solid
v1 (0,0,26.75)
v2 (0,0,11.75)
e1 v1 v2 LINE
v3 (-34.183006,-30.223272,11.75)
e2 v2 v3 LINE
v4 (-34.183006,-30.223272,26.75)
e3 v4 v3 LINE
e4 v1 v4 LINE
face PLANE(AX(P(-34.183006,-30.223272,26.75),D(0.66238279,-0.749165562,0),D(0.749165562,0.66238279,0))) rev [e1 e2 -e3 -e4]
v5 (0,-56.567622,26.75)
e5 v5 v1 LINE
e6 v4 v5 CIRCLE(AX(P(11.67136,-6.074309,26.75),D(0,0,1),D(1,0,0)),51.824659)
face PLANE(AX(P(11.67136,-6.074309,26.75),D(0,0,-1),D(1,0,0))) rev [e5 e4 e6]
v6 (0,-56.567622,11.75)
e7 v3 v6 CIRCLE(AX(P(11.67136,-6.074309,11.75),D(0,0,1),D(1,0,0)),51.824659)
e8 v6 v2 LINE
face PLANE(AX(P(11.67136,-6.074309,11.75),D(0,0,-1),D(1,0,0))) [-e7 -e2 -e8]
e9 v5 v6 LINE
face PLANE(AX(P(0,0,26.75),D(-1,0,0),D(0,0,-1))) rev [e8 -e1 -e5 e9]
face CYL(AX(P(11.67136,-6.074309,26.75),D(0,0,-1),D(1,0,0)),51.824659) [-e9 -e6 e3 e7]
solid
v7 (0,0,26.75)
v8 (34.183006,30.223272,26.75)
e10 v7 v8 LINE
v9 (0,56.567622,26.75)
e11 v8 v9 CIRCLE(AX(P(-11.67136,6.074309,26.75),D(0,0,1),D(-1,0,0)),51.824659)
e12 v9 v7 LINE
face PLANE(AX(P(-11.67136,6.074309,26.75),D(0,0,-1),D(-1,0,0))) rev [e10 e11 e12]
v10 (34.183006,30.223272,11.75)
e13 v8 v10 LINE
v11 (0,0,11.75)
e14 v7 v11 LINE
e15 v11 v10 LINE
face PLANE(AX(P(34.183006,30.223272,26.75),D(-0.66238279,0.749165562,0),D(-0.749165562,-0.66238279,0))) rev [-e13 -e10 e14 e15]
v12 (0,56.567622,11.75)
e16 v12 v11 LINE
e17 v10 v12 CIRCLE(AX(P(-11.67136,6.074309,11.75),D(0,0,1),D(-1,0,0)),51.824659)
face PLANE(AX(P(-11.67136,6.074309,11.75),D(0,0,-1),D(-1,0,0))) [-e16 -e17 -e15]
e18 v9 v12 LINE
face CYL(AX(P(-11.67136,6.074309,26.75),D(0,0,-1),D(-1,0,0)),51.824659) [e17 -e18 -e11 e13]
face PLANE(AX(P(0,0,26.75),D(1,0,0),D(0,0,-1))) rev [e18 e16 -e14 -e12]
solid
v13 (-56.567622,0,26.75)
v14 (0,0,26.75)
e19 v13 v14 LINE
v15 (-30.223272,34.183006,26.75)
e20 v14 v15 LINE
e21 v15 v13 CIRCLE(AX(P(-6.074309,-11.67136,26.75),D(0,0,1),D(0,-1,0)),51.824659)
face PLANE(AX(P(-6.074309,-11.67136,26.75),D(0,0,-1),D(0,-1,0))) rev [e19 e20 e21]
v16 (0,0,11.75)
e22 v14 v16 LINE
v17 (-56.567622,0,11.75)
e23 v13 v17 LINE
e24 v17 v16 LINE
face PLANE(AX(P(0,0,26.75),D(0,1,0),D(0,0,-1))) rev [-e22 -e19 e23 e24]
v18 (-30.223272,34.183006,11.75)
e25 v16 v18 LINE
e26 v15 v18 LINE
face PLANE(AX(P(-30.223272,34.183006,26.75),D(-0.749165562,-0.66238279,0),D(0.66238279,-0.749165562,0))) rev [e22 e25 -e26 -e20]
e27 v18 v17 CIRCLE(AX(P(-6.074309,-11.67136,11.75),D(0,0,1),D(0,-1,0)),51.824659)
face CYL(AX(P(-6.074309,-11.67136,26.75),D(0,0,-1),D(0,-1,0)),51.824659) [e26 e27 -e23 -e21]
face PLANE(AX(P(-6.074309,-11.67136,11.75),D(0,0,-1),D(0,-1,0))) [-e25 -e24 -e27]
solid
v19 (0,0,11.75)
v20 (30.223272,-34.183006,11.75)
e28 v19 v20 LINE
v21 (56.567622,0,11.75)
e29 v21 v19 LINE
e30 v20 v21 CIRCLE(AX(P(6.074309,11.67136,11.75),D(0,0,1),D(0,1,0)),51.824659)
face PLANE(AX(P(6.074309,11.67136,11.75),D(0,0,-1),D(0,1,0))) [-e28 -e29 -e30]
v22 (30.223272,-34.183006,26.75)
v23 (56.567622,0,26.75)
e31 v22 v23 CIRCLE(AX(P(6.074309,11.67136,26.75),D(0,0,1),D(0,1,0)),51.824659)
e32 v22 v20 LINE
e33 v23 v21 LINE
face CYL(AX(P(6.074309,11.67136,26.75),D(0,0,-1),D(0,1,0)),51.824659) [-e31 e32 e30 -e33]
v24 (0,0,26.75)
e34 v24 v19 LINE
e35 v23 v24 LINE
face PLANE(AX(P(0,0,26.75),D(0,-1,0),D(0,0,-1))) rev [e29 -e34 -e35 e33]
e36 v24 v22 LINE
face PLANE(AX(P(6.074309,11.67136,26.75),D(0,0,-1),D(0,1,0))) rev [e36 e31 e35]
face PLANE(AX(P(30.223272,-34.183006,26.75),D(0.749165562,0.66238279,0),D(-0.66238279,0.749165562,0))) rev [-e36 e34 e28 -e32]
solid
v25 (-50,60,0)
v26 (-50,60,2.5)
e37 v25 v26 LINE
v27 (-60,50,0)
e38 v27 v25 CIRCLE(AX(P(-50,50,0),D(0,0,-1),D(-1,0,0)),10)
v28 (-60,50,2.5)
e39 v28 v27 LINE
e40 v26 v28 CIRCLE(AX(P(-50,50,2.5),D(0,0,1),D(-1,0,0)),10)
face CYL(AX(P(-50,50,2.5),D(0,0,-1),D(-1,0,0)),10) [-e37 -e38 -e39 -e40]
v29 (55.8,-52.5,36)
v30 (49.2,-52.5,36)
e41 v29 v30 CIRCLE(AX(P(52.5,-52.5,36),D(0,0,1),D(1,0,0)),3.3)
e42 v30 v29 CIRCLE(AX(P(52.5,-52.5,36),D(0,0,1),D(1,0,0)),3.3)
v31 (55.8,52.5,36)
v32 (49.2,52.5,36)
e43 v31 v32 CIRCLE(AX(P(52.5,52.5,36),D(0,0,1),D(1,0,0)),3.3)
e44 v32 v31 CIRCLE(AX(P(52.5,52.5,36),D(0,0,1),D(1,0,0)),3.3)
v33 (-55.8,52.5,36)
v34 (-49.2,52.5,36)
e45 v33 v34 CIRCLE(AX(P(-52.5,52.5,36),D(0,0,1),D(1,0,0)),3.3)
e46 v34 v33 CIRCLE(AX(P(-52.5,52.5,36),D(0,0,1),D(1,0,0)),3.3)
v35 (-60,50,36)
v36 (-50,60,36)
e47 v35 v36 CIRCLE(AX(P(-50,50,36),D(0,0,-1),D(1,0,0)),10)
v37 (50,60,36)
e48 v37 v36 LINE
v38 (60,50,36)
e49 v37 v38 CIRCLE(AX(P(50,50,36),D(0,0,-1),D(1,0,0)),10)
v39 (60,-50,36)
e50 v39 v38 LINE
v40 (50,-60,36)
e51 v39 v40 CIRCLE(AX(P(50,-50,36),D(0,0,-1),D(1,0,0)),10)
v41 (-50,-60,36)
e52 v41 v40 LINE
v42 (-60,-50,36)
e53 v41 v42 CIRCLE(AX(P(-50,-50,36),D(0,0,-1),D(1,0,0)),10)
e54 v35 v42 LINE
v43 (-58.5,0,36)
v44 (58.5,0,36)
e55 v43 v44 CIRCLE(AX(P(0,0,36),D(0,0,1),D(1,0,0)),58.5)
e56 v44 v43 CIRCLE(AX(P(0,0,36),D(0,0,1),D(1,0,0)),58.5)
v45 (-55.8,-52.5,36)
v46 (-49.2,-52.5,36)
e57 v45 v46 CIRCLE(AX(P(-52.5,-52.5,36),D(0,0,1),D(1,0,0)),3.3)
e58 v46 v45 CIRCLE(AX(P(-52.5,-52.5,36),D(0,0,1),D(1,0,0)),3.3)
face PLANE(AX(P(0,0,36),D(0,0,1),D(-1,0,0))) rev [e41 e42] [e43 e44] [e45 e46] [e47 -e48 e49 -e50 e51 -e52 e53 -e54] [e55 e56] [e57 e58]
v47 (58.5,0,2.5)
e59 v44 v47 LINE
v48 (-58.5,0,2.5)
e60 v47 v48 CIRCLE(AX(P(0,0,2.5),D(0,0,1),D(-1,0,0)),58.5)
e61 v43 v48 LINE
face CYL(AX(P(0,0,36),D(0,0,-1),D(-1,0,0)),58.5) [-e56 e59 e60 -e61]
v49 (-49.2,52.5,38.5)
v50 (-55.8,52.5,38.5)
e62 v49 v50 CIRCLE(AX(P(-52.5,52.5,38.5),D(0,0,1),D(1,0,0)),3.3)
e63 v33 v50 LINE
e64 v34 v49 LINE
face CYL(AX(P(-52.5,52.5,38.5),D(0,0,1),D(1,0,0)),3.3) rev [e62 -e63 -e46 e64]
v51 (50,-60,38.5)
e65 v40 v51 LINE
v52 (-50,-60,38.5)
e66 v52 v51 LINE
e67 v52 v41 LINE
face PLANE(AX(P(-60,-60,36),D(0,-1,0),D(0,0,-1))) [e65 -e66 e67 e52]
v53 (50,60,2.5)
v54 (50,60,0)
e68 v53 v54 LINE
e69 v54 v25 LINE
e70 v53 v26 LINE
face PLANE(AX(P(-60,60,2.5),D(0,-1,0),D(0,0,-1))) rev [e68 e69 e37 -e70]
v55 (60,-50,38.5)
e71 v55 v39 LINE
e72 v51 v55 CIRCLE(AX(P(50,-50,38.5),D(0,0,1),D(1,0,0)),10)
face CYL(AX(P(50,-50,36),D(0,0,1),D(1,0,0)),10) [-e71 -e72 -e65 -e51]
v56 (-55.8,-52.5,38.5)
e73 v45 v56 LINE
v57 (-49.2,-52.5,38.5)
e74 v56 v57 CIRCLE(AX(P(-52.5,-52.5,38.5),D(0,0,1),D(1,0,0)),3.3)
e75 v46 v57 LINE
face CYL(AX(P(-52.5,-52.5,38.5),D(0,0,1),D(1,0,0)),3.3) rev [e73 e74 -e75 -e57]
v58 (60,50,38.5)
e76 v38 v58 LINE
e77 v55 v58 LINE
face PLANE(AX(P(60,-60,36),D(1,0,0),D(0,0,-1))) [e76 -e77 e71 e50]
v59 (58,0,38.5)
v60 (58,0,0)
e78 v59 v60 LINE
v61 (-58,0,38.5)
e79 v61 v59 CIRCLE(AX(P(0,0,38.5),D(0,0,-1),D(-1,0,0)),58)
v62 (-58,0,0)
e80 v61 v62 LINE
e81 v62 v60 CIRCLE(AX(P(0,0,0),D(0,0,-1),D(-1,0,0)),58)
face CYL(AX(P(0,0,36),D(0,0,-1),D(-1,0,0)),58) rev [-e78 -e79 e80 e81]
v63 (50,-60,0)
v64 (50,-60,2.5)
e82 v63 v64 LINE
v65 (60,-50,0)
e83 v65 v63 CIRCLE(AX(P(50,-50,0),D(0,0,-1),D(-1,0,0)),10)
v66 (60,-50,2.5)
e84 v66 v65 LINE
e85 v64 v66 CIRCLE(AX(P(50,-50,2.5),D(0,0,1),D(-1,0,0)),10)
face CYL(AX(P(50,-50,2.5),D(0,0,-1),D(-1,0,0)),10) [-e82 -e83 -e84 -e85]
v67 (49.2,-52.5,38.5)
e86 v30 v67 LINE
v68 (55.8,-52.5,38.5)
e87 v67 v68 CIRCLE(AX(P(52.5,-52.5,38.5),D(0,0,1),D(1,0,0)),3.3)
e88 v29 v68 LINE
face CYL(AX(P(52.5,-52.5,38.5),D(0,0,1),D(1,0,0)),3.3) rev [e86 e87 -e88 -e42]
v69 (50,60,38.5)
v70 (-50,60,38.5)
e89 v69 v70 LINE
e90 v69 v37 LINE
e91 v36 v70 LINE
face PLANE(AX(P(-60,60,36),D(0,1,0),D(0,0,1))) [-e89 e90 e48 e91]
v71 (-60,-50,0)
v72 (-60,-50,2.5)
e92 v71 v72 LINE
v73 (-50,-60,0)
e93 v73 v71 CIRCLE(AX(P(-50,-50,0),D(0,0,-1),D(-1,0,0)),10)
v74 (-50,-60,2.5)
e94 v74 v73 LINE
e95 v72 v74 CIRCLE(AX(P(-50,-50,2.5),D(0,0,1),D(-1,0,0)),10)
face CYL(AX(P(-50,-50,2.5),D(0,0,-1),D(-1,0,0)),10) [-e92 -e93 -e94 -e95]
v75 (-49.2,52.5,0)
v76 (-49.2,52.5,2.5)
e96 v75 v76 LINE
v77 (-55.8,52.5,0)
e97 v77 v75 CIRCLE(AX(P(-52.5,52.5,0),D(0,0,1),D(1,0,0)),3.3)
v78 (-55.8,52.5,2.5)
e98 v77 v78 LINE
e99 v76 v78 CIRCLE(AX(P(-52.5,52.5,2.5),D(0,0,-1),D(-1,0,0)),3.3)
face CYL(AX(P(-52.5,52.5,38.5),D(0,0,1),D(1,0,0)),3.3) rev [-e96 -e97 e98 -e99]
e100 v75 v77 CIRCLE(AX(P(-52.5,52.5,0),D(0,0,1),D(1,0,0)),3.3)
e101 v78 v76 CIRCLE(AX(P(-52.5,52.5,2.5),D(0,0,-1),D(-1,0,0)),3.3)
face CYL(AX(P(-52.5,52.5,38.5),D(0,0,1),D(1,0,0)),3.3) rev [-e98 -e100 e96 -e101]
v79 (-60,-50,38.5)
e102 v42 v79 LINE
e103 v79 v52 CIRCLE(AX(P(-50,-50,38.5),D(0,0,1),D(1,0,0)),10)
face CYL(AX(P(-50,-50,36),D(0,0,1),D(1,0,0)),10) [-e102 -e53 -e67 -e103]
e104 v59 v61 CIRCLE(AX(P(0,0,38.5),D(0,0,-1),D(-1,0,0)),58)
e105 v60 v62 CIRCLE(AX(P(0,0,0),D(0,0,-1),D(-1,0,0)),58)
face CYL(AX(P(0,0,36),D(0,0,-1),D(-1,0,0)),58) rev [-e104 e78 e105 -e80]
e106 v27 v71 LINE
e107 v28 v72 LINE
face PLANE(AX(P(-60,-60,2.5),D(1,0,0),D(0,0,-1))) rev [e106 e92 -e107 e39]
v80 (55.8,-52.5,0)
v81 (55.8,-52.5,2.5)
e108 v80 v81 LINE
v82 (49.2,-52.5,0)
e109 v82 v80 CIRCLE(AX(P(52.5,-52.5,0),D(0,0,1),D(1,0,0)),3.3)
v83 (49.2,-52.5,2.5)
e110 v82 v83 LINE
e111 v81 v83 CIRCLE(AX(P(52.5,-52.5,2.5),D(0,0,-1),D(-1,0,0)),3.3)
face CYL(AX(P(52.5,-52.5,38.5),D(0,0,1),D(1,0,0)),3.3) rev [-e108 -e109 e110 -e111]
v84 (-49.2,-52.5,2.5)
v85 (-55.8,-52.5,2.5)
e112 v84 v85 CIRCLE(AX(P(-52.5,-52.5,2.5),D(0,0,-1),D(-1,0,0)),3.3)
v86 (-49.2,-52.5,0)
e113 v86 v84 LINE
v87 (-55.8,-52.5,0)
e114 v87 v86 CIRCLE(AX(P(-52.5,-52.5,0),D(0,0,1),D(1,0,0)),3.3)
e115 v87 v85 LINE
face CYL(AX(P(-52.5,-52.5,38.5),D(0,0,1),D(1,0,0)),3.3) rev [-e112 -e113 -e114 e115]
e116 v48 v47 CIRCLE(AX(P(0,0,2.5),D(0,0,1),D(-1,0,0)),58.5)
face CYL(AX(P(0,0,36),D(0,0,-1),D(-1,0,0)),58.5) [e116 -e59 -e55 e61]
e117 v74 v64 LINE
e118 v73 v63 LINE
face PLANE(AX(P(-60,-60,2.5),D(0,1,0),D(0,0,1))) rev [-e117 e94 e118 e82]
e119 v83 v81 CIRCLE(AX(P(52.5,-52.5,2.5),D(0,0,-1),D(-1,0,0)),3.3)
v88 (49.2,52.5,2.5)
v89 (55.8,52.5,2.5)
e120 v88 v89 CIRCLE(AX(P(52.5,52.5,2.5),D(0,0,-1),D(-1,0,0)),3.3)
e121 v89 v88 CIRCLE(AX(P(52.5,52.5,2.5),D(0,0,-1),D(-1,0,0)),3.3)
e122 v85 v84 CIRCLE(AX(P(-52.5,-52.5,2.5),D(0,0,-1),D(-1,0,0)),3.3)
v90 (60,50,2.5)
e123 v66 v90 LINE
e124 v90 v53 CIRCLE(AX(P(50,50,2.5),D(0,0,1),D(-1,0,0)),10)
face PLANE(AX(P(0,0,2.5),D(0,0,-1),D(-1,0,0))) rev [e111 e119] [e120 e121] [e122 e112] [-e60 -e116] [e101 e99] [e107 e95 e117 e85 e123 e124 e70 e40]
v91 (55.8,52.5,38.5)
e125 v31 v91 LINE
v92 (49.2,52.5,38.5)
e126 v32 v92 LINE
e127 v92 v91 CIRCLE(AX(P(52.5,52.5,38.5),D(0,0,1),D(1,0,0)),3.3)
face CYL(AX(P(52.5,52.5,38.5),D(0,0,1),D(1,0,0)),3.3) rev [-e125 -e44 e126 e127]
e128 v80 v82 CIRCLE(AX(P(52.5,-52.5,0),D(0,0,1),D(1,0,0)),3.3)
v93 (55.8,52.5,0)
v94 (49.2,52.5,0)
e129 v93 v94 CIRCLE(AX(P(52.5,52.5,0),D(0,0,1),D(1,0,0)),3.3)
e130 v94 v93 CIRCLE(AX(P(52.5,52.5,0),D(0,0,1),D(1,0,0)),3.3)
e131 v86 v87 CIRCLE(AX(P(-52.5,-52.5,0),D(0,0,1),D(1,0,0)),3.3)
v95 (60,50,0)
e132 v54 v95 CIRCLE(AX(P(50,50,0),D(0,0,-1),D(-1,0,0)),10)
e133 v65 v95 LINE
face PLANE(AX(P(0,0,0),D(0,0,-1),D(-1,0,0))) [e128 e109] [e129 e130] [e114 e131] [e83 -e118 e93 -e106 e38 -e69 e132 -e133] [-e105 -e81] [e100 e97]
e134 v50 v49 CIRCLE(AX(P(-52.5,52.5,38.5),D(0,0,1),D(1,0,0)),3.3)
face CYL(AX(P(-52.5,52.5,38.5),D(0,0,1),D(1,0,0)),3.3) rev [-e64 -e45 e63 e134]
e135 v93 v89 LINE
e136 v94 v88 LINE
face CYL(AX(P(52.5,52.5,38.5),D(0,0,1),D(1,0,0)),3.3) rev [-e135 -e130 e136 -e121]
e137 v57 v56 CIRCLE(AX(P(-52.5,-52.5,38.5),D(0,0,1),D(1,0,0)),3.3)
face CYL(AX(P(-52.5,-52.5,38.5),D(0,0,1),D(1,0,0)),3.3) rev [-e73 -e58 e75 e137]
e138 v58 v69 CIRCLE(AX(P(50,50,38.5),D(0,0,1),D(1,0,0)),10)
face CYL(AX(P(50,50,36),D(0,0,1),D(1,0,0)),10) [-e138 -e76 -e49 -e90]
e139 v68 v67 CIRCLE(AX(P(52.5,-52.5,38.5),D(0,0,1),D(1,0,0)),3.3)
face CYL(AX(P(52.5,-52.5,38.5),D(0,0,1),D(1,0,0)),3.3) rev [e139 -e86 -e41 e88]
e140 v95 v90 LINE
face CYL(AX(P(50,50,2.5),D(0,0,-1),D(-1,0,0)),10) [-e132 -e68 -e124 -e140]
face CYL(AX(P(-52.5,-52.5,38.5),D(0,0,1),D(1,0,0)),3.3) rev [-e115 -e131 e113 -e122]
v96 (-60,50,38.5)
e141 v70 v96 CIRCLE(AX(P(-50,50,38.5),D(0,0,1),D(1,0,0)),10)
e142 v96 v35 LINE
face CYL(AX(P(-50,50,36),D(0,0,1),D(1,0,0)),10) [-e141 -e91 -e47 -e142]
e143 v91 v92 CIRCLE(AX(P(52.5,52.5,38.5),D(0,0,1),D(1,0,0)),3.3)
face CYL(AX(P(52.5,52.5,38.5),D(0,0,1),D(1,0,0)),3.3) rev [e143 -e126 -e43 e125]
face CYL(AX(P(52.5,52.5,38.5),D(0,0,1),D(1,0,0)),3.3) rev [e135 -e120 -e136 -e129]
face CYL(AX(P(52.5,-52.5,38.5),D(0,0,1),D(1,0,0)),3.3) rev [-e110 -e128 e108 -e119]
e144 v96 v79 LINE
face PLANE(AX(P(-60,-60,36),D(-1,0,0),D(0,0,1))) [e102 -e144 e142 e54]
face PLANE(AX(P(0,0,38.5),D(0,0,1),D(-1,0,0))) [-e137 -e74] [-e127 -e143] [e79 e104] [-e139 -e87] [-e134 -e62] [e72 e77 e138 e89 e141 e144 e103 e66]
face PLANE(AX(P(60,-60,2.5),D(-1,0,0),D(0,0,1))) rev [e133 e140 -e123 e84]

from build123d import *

# Parameters (mm, degrees)
SKETCH_1_W                  = 120
SKETCH_1_H                  = 120
EXTRUDE_1_DEPTH             = 2.5
SKETCH_2_R                  = 58.5
SKETCH_2_R_2                = 56.5
EXTRUDE_2_DEPTH             = 33.5
SKETCH_4_R                  = 58
CUT_EXTRUDE_1_DEPTH         = 93.173748974
FILLET_1_R                  = 10
FILLET_1_OF_MIRROR_1_R      = 10
EXTRUDE_3_DEPTH             = 7.5
PATTERN_CIRCULAR_2_COUNT    = 4
SKETCH_9_W                  = 3.3
SKETCH_9_H                  = 38.5
HOLE_WIZARD_M6_1_AT_2_COUNT = 2
HOLE_WIZARD_M6_1_AT_2_PITCH = 105
HOLE_WIZARD_M6_1_AT_3_COUNT = 2
HOLE_WIZARD_M6_1_AT_3_PITCH = 148.492424049
HOLE_WIZARD_M6_1_AT_4_COUNT = 2
HOLE_WIZARD_M6_1_AT_4_PITCH = 105


with BuildPart() as part:
    # 草图1 → 凸台-拉伸1 (new body)
    with BuildSketch(Plane.XY):
        Rectangle(SKETCH_1_W, SKETCH_1_H)
    extrude_1 = extrude(amount=EXTRUDE_1_DEPTH)

    # 草图2 → 凸台-拉伸2 (add)
    with BuildSketch(Plane.XY.offset(2.5)):
        with Locations(Location((0, 0, 0), (0, 0, 180))):
            Circle(SKETCH_2_R)
        Circle(SKETCH_2_R_2, mode=Mode.SUBTRACT)
    extrude(amount=EXTRUDE_2_DEPTH)

    # 草图4 → 切除-拉伸1 (cut, through all)
    with BuildSketch(Plane(origin=(0, 0, 0), x_dir=(-1, 0, 0), z_dir=(0, 0, -1))):
        Circle(SKETCH_4_R)
    cut_extrude_1 = extrude(amount=-CUT_EXTRUDE_1_DEPTH, mode=Mode.SUBTRACT)

    # 圆角1
    fillet_1_edges = [part.edges().sort_by_distance(p)[0] for p in [
        (60, -60, 1.25),
        (-60, -60, 1.25),
        (-60, 60, 1.25),
        (60, 60, 1.25),
    ]]
    fillet(fillet_1_edges, radius=FILLET_1_R)

    # 镜向1: 凸台-拉伸1, 切除-拉伸1 across plane
    add(extrude_1.mirror(Plane.XY.offset(19.25)))
    add(cut_extrude_1.mirror(Plane.XY.offset(19.25)), mode=Mode.SUBTRACT)

    # 圆角1 of 镜向1
    fillet_1_of_mirror_1_edges = [part.edges().sort_by_distance(p)[0] for p in [
        (60, -60, 37.25),
        (-60, -60, 37.25),
        (-60, 60, 37.25),
        (60, 60, 37.25),
    ]]
    fillet(fillet_1_of_mirror_1_edges, radius=FILLET_1_OF_MIRROR_1_R)

    # 草图9 → M6 间隙孔1 (revolve, cut)
    with BuildSketch(Plane(origin=(-52.5, 52.5, 38.5), x_dir=(0, -1, 0), z_dir=(1, 0, 0))):
        with Locations((1.65, 19.25)):
            Rectangle(SKETCH_9_W, SKETCH_9_H)
    hole_wizard_m6_1 = revolve(axis=Axis((-52.5, 52.5, 44.85), (0, 0, -1)), mode=Mode.SUBTRACT)

    # M6 间隙孔1 at 2: M6 间隙孔1 ×2
    with Locations(*[(i * HOLE_WIZARD_M6_1_AT_2_PITCH, 0, 0) for i in range(1, HOLE_WIZARD_M6_1_AT_2_COUNT)]):
        add(hole_wizard_m6_1, mode=Mode.SUBTRACT)

    # M6 间隙孔1 at 3: M6 间隙孔1 ×2
    with Locations(*[Vector(0.7071067811865476, -0.7071067811865476, 0) * (i * HOLE_WIZARD_M6_1_AT_3_PITCH) for i in range(1, HOLE_WIZARD_M6_1_AT_3_COUNT)]):
        add(hole_wizard_m6_1, mode=Mode.SUBTRACT)

    # M6 间隙孔1 at 4: M6 间隙孔1 ×2
    with Locations(*[(0, -i * HOLE_WIZARD_M6_1_AT_4_PITCH, 0) for i in range(1, HOLE_WIZARD_M6_1_AT_4_COUNT)]):
        add(hole_wizard_m6_1, mode=Mode.SUBTRACT)


with BuildPart() as body_2:
    # 草图6 → 凸台-拉伸3 (new, symmetric)
    with BuildSketch(Plane.XY.offset(19.25)):
        with BuildLine():
            Line((0, 0), (0, 56.567621743))
            ThreePointArc((0, 56.567621743), (19.964197037, 47.122899845), (34.18300571, 30.223272188))
            Line((34.18300571, 30.223272188), (0, 0))
        make_face()
    extrude(amount=EXTRUDE_3_DEPTH, both=True)


with BuildPart() as pattern_circular_2_1:
    # 阵列(圆周)2: pattern copy
    add(body_2.part.rotate(Axis((0, 0, 0), (0, 0, 1)), 1 * 360 / PATTERN_CIRCULAR_2_COUNT))


with BuildPart() as pattern_circular_2_2:
    # 阵列(圆周)2: pattern copy
    add(body_2.part.rotate(Axis((0, 0, 0), (0, 0, 1)), 2 * 360 / PATTERN_CIRCULAR_2_COUNT))


with BuildPart() as pattern_circular_2_3:
    # 阵列(圆周)2: pattern copy
    add(body_2.part.rotate(Axis((0, 0, 0), (0, 0, 1)), 3 * 360 / PATTERN_CIRCULAR_2_COUNT))


solid = Compound([part.part, body_2.part, pattern_circular_2_1.part, pattern_circular_2_2.part, pattern_circular_2_3.part])
